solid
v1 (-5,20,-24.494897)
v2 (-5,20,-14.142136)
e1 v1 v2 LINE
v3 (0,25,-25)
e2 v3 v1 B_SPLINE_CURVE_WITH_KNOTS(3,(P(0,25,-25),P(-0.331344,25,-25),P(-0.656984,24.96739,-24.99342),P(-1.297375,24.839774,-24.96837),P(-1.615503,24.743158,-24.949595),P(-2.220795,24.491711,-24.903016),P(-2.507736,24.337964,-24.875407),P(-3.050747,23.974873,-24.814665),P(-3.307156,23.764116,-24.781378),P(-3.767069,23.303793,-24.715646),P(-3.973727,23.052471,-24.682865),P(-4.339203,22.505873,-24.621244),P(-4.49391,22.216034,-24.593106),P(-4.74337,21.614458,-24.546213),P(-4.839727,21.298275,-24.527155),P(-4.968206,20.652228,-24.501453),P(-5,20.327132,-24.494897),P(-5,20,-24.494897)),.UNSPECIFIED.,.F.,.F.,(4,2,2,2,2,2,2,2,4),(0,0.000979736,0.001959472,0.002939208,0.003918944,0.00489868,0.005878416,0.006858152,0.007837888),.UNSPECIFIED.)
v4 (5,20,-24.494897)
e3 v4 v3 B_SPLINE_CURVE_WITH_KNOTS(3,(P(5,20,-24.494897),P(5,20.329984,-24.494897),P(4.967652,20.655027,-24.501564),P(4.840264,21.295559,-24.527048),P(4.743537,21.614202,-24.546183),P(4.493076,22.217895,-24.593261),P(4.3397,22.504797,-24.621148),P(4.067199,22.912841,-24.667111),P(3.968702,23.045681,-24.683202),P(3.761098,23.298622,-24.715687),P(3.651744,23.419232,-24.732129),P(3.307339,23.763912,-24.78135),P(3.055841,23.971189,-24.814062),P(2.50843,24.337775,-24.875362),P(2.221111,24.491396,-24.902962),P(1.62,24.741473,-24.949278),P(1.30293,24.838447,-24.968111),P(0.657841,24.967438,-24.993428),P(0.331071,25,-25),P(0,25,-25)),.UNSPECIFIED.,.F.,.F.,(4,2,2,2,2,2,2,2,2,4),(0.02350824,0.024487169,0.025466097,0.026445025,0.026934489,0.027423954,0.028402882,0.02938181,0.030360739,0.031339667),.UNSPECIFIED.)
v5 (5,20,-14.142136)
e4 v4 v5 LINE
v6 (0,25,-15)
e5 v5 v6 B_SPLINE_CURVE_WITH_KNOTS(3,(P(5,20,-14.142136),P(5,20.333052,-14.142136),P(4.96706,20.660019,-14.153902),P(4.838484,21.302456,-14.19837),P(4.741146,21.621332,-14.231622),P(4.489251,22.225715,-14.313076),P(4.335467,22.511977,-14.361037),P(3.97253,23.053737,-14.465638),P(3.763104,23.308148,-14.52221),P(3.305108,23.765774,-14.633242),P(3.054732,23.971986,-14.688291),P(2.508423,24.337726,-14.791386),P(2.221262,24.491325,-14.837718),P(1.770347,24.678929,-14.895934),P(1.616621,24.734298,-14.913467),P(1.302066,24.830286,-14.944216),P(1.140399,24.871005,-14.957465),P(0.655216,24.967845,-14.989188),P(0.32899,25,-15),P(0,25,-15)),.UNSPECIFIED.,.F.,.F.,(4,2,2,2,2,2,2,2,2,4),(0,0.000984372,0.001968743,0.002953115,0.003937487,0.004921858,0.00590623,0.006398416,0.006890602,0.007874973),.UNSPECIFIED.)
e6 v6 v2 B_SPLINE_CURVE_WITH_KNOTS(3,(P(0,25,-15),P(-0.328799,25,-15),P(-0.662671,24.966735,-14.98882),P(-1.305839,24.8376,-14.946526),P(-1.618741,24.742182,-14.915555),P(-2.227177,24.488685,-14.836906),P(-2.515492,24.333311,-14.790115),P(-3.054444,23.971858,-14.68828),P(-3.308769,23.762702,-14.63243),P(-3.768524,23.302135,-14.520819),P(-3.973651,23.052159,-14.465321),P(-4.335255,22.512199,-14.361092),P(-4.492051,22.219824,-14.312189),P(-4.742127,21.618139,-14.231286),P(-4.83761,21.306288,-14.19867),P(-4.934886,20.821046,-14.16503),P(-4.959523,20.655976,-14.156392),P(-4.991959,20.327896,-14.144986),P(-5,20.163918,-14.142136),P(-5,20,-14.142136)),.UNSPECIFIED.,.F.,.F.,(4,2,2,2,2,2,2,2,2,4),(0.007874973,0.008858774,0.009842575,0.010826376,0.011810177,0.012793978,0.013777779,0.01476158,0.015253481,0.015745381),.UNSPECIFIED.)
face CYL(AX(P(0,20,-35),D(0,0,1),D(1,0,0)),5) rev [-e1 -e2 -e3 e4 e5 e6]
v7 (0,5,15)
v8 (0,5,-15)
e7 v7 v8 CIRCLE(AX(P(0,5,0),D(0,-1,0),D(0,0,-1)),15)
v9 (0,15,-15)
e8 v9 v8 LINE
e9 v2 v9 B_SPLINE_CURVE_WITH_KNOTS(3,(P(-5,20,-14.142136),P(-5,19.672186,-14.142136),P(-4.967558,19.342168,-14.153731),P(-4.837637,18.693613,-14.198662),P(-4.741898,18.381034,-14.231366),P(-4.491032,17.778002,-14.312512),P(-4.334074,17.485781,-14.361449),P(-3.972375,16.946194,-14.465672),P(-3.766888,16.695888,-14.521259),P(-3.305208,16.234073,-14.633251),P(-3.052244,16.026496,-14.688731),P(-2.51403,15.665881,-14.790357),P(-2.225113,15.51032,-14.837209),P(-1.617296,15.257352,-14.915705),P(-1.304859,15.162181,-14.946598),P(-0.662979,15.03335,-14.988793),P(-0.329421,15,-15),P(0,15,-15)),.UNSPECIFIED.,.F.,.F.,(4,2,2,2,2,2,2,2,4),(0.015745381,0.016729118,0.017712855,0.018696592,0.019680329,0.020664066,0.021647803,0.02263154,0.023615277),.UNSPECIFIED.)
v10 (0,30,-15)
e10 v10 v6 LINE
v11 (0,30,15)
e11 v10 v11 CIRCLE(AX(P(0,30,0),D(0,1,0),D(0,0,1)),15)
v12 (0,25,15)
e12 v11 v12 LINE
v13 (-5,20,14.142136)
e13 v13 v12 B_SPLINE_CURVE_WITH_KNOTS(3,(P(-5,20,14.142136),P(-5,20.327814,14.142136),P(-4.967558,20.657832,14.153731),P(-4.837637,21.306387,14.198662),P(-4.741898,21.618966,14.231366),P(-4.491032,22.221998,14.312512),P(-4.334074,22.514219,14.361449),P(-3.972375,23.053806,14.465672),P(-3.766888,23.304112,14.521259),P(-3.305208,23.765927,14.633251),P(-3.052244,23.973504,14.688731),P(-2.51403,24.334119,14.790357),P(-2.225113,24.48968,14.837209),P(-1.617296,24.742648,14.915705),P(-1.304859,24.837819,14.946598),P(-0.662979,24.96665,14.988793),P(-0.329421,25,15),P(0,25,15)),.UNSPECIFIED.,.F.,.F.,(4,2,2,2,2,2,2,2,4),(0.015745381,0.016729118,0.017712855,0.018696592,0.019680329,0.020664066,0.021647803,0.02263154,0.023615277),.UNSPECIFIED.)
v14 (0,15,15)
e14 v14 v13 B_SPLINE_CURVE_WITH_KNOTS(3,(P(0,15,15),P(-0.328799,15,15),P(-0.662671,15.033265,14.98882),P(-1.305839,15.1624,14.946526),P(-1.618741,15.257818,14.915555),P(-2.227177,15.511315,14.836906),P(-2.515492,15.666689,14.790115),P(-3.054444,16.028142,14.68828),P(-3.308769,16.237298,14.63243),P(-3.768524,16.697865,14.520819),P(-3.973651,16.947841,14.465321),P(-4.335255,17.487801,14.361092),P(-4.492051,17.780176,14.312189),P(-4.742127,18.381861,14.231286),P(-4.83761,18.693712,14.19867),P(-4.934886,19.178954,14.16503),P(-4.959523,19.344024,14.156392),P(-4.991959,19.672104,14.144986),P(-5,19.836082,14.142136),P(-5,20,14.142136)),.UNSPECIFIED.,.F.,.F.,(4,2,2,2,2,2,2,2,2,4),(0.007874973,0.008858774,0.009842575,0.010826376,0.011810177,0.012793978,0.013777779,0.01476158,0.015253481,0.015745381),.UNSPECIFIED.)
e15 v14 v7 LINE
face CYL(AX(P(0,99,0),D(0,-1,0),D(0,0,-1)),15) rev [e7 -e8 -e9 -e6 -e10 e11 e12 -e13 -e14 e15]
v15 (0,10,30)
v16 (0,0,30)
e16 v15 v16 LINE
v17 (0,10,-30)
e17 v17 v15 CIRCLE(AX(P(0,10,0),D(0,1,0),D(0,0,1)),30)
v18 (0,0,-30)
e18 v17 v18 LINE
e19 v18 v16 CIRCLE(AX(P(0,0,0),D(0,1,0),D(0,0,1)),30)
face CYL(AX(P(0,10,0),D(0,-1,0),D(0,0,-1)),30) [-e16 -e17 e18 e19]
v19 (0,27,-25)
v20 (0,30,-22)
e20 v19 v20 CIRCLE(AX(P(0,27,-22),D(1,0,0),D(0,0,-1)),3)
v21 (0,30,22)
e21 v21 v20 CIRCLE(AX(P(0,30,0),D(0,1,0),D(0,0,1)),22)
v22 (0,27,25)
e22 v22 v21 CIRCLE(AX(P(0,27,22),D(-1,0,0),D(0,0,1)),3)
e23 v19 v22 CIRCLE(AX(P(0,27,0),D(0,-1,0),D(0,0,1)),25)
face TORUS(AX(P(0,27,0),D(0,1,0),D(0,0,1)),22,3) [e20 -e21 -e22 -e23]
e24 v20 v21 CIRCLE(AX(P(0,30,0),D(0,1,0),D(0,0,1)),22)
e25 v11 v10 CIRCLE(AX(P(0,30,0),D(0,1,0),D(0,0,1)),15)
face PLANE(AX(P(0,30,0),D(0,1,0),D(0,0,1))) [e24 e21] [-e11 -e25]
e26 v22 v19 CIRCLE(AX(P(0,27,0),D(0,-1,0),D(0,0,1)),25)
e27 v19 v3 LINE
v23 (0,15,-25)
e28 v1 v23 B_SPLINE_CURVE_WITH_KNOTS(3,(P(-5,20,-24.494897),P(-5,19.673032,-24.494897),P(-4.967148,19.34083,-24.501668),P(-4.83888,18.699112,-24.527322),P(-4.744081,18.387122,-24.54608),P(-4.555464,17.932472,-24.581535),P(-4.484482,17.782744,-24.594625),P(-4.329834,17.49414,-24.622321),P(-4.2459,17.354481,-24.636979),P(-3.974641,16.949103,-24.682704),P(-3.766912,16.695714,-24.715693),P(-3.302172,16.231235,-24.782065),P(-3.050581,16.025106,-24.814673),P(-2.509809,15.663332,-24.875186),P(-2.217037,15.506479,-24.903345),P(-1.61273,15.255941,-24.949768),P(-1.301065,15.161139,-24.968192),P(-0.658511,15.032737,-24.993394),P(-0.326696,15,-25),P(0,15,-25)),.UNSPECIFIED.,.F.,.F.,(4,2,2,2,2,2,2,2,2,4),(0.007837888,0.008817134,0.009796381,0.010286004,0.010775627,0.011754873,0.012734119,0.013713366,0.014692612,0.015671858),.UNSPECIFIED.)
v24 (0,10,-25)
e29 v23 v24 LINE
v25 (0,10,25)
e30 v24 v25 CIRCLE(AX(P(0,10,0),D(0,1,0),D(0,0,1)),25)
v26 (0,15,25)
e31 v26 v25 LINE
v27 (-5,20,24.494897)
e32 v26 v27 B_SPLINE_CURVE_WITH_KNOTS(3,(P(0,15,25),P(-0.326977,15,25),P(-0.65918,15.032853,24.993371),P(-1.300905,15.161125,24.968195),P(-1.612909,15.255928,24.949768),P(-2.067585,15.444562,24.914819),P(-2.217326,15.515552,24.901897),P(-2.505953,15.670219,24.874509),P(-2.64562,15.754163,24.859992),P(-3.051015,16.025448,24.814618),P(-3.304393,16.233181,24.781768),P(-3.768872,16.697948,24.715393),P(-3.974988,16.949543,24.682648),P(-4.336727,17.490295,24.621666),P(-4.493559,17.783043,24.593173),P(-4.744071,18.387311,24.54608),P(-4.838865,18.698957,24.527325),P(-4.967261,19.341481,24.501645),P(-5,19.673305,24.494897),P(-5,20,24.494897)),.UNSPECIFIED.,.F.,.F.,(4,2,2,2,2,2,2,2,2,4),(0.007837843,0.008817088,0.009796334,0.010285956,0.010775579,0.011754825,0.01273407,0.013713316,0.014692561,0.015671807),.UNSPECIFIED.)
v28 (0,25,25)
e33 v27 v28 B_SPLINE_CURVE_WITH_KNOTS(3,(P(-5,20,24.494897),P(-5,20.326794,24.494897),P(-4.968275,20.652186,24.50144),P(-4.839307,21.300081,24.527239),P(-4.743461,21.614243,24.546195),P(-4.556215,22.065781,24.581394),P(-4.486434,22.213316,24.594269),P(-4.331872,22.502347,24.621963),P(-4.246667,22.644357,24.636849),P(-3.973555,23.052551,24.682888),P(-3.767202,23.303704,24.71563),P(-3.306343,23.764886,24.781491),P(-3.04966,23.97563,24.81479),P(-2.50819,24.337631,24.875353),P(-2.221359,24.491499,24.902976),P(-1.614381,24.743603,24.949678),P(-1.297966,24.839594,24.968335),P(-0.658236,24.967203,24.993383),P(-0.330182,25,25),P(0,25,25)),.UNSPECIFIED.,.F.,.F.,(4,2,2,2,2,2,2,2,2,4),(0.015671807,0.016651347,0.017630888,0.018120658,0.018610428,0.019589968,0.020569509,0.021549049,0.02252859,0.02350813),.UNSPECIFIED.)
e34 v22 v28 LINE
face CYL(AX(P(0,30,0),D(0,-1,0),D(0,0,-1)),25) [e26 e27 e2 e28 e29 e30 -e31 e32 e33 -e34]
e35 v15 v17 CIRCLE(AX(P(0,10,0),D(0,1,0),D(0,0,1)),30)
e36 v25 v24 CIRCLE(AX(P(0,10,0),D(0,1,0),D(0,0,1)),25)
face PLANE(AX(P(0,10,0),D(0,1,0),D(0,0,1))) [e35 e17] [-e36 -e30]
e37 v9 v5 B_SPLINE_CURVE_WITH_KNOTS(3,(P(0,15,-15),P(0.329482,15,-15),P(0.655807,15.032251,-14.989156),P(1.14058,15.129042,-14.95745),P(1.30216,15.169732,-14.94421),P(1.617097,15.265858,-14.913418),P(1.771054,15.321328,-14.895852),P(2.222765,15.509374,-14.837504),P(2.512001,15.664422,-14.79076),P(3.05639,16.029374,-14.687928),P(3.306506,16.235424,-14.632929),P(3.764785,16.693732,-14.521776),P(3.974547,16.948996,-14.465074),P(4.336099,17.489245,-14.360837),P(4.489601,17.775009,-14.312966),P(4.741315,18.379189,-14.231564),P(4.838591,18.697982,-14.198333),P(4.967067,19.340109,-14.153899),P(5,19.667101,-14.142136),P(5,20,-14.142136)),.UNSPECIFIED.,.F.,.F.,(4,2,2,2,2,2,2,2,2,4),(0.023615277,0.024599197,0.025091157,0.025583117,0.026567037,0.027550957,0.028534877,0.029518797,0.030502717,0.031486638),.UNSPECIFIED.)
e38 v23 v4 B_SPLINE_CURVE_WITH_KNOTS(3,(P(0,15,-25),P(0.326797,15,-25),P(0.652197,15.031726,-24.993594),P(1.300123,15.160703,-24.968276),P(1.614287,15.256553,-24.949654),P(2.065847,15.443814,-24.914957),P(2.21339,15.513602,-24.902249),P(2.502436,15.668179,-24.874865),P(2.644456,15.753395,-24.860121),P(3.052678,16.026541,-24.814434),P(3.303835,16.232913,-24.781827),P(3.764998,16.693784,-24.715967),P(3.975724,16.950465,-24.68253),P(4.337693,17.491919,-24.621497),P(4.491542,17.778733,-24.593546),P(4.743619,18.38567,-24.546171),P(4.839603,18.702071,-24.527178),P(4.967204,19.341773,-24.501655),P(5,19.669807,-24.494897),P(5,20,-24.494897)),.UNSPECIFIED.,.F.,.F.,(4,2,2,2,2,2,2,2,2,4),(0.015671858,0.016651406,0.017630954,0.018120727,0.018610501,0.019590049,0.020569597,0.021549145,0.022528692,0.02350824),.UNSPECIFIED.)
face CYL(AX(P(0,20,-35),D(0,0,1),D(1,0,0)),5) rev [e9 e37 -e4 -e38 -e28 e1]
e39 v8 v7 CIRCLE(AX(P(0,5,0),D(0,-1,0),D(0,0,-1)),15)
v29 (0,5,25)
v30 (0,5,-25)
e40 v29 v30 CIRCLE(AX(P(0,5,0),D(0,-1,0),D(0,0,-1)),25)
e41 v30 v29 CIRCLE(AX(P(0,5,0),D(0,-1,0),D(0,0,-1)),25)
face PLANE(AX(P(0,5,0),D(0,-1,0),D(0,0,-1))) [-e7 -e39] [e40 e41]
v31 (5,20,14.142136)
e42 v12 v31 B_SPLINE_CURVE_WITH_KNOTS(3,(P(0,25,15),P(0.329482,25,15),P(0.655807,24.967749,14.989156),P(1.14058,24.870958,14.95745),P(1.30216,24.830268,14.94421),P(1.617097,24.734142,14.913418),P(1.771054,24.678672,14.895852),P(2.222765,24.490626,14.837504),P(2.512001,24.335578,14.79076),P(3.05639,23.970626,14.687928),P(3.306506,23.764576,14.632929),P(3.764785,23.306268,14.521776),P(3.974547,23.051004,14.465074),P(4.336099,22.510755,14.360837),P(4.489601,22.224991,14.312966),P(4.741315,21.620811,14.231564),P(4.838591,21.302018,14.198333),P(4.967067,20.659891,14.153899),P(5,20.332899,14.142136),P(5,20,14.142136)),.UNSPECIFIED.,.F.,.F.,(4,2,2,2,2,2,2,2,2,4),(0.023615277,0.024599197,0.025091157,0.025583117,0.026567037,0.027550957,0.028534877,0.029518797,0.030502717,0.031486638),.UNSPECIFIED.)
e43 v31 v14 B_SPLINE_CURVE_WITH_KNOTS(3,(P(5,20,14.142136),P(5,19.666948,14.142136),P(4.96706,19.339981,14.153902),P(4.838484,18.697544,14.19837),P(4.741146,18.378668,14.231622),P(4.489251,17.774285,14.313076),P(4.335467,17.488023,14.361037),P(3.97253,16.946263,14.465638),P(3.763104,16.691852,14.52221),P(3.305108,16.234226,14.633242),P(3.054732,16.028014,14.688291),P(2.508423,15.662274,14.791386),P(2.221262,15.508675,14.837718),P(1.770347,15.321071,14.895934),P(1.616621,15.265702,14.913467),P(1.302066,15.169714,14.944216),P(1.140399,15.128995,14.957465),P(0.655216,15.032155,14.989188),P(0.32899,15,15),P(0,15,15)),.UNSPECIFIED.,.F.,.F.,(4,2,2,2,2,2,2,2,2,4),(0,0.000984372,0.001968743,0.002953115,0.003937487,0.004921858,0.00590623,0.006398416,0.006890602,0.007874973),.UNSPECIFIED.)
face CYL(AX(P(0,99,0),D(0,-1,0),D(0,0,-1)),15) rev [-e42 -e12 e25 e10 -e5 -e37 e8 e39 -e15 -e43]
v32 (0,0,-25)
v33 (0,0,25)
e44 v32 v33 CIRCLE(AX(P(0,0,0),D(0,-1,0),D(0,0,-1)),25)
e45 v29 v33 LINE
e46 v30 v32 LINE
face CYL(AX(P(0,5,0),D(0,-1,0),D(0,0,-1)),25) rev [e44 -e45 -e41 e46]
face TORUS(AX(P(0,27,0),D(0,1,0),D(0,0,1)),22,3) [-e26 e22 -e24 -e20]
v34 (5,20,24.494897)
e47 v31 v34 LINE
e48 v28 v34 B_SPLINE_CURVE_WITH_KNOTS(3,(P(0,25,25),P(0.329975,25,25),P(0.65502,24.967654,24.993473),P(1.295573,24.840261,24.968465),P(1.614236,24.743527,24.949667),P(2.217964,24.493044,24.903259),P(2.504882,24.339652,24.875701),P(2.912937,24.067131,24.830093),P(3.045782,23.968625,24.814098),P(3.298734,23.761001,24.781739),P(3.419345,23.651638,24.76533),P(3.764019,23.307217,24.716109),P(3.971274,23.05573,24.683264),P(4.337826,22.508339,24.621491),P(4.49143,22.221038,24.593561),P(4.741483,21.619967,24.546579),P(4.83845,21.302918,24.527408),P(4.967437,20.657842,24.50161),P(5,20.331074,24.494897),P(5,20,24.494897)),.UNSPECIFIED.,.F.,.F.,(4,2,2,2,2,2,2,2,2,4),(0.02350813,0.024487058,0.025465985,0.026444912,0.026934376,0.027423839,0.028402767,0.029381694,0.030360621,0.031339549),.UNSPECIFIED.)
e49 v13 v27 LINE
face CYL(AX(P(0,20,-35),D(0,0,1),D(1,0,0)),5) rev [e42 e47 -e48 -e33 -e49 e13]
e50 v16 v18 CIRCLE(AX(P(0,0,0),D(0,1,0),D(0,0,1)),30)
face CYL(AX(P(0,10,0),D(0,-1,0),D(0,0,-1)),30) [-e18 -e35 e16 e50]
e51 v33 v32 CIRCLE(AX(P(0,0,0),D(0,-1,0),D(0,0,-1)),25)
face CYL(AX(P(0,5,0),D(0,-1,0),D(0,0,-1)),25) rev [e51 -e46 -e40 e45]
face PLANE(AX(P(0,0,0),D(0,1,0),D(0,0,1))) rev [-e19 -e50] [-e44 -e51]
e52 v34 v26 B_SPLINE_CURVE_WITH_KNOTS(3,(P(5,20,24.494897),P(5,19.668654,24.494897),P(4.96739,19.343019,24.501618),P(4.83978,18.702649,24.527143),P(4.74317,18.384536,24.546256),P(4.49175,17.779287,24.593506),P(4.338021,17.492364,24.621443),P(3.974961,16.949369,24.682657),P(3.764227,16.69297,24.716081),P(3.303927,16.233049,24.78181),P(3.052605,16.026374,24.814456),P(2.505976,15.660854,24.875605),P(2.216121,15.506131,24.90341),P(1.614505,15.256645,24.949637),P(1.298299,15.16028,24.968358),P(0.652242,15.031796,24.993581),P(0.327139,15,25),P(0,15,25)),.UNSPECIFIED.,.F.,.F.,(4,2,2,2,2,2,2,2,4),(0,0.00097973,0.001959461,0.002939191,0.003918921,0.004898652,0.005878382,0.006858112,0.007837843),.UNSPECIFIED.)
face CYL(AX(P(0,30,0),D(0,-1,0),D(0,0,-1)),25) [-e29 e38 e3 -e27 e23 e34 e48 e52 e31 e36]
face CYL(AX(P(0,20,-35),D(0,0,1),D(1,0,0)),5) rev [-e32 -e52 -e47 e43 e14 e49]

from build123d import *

# Parameters (mm, degrees)
FLANGE_PROFILE_60_R      = 30
BASE_FLANGE_60X10_DEPTH  = 10
BOSS_PROFILE_50_R        = 25
COLLAR_BOSS_50X20_DEPTH  = 20
BOSS_EDGE_FILLET_R3_R    = 3
CROSS_HOLE_PROFILE_10_R  = 5
CROSS_HOLE_10_DEPTH      = 35
COUNTERBORE_PROFILE_50_R = 25
COUNTERBORE_50X5_DEPTH   = 5
BORE_PROFILE_30_R        = 15
THROUGH_BORE_30_DEPTH    = 94


with BuildPart() as part:
    # Flange Profile Ø60 → Base Flange Ø60x10 (new body)
    with BuildSketch(Plane(origin=(0, 0, 0), x_dir=(1, 0, 0), z_dir=(0, 1, 0))):
        with Locations(Location((0, 0, 0), (0, 0, 270))):
            Circle(FLANGE_PROFILE_60_R)
    extrude(amount=BASE_FLANGE_60X10_DEPTH)

    # Boss Profile Ø50 → Collar Boss Ø50x20 (add)
    with BuildSketch(Plane(origin=(0, 10, 0), x_dir=(1, 0, 0), z_dir=(0, 1, 0))):
        with Locations(Location((0, 0, 0), (0, 0, 270))):
            Circle(BOSS_PROFILE_50_R)
    extrude(amount=COLLAR_BOSS_50X20_DEPTH)

    # Boss Edge Fillet R3
    boss_edge_fillet_r3_edges = [part.edges().sort_by_distance(p)[0] for p in [
        (0, 30, -25),
    ]]
    fillet(boss_edge_fillet_r3_edges, radius=BOSS_EDGE_FILLET_R3_R)

    # Cross Hole Profile Ø10 → Cross Hole Ø10 (cut, symmetric)
    with BuildSketch(Plane.XY):
        with Locations((0, 20)):
            Circle(CROSS_HOLE_PROFILE_10_R)
    extrude(amount=CROSS_HOLE_10_DEPTH, both=True, mode=Mode.SUBTRACT)

    # Counterbore Profile Ø50 → Counterbore Ø50x5 (cut)
    with BuildSketch(Plane.XZ):
        with Locations(Location((0, 0, 0), (0, 0, 90))):
            Circle(COUNTERBORE_PROFILE_50_R)
    extrude(amount=-COUNTERBORE_50X5_DEPTH, mode=Mode.SUBTRACT)

    # Bore Profile Ø30 → Through Bore Ø30 (cut)
    with BuildSketch(Plane.XZ.offset(-5)):
        with Locations(Location((0, 0, 0), (0, 0, 270))):
            Circle(BORE_PROFILE_30_R)
    extrude(amount=-THROUGH_BORE_30_DEPTH, mode=Mode.SUBTRACT)


solid = part.part
